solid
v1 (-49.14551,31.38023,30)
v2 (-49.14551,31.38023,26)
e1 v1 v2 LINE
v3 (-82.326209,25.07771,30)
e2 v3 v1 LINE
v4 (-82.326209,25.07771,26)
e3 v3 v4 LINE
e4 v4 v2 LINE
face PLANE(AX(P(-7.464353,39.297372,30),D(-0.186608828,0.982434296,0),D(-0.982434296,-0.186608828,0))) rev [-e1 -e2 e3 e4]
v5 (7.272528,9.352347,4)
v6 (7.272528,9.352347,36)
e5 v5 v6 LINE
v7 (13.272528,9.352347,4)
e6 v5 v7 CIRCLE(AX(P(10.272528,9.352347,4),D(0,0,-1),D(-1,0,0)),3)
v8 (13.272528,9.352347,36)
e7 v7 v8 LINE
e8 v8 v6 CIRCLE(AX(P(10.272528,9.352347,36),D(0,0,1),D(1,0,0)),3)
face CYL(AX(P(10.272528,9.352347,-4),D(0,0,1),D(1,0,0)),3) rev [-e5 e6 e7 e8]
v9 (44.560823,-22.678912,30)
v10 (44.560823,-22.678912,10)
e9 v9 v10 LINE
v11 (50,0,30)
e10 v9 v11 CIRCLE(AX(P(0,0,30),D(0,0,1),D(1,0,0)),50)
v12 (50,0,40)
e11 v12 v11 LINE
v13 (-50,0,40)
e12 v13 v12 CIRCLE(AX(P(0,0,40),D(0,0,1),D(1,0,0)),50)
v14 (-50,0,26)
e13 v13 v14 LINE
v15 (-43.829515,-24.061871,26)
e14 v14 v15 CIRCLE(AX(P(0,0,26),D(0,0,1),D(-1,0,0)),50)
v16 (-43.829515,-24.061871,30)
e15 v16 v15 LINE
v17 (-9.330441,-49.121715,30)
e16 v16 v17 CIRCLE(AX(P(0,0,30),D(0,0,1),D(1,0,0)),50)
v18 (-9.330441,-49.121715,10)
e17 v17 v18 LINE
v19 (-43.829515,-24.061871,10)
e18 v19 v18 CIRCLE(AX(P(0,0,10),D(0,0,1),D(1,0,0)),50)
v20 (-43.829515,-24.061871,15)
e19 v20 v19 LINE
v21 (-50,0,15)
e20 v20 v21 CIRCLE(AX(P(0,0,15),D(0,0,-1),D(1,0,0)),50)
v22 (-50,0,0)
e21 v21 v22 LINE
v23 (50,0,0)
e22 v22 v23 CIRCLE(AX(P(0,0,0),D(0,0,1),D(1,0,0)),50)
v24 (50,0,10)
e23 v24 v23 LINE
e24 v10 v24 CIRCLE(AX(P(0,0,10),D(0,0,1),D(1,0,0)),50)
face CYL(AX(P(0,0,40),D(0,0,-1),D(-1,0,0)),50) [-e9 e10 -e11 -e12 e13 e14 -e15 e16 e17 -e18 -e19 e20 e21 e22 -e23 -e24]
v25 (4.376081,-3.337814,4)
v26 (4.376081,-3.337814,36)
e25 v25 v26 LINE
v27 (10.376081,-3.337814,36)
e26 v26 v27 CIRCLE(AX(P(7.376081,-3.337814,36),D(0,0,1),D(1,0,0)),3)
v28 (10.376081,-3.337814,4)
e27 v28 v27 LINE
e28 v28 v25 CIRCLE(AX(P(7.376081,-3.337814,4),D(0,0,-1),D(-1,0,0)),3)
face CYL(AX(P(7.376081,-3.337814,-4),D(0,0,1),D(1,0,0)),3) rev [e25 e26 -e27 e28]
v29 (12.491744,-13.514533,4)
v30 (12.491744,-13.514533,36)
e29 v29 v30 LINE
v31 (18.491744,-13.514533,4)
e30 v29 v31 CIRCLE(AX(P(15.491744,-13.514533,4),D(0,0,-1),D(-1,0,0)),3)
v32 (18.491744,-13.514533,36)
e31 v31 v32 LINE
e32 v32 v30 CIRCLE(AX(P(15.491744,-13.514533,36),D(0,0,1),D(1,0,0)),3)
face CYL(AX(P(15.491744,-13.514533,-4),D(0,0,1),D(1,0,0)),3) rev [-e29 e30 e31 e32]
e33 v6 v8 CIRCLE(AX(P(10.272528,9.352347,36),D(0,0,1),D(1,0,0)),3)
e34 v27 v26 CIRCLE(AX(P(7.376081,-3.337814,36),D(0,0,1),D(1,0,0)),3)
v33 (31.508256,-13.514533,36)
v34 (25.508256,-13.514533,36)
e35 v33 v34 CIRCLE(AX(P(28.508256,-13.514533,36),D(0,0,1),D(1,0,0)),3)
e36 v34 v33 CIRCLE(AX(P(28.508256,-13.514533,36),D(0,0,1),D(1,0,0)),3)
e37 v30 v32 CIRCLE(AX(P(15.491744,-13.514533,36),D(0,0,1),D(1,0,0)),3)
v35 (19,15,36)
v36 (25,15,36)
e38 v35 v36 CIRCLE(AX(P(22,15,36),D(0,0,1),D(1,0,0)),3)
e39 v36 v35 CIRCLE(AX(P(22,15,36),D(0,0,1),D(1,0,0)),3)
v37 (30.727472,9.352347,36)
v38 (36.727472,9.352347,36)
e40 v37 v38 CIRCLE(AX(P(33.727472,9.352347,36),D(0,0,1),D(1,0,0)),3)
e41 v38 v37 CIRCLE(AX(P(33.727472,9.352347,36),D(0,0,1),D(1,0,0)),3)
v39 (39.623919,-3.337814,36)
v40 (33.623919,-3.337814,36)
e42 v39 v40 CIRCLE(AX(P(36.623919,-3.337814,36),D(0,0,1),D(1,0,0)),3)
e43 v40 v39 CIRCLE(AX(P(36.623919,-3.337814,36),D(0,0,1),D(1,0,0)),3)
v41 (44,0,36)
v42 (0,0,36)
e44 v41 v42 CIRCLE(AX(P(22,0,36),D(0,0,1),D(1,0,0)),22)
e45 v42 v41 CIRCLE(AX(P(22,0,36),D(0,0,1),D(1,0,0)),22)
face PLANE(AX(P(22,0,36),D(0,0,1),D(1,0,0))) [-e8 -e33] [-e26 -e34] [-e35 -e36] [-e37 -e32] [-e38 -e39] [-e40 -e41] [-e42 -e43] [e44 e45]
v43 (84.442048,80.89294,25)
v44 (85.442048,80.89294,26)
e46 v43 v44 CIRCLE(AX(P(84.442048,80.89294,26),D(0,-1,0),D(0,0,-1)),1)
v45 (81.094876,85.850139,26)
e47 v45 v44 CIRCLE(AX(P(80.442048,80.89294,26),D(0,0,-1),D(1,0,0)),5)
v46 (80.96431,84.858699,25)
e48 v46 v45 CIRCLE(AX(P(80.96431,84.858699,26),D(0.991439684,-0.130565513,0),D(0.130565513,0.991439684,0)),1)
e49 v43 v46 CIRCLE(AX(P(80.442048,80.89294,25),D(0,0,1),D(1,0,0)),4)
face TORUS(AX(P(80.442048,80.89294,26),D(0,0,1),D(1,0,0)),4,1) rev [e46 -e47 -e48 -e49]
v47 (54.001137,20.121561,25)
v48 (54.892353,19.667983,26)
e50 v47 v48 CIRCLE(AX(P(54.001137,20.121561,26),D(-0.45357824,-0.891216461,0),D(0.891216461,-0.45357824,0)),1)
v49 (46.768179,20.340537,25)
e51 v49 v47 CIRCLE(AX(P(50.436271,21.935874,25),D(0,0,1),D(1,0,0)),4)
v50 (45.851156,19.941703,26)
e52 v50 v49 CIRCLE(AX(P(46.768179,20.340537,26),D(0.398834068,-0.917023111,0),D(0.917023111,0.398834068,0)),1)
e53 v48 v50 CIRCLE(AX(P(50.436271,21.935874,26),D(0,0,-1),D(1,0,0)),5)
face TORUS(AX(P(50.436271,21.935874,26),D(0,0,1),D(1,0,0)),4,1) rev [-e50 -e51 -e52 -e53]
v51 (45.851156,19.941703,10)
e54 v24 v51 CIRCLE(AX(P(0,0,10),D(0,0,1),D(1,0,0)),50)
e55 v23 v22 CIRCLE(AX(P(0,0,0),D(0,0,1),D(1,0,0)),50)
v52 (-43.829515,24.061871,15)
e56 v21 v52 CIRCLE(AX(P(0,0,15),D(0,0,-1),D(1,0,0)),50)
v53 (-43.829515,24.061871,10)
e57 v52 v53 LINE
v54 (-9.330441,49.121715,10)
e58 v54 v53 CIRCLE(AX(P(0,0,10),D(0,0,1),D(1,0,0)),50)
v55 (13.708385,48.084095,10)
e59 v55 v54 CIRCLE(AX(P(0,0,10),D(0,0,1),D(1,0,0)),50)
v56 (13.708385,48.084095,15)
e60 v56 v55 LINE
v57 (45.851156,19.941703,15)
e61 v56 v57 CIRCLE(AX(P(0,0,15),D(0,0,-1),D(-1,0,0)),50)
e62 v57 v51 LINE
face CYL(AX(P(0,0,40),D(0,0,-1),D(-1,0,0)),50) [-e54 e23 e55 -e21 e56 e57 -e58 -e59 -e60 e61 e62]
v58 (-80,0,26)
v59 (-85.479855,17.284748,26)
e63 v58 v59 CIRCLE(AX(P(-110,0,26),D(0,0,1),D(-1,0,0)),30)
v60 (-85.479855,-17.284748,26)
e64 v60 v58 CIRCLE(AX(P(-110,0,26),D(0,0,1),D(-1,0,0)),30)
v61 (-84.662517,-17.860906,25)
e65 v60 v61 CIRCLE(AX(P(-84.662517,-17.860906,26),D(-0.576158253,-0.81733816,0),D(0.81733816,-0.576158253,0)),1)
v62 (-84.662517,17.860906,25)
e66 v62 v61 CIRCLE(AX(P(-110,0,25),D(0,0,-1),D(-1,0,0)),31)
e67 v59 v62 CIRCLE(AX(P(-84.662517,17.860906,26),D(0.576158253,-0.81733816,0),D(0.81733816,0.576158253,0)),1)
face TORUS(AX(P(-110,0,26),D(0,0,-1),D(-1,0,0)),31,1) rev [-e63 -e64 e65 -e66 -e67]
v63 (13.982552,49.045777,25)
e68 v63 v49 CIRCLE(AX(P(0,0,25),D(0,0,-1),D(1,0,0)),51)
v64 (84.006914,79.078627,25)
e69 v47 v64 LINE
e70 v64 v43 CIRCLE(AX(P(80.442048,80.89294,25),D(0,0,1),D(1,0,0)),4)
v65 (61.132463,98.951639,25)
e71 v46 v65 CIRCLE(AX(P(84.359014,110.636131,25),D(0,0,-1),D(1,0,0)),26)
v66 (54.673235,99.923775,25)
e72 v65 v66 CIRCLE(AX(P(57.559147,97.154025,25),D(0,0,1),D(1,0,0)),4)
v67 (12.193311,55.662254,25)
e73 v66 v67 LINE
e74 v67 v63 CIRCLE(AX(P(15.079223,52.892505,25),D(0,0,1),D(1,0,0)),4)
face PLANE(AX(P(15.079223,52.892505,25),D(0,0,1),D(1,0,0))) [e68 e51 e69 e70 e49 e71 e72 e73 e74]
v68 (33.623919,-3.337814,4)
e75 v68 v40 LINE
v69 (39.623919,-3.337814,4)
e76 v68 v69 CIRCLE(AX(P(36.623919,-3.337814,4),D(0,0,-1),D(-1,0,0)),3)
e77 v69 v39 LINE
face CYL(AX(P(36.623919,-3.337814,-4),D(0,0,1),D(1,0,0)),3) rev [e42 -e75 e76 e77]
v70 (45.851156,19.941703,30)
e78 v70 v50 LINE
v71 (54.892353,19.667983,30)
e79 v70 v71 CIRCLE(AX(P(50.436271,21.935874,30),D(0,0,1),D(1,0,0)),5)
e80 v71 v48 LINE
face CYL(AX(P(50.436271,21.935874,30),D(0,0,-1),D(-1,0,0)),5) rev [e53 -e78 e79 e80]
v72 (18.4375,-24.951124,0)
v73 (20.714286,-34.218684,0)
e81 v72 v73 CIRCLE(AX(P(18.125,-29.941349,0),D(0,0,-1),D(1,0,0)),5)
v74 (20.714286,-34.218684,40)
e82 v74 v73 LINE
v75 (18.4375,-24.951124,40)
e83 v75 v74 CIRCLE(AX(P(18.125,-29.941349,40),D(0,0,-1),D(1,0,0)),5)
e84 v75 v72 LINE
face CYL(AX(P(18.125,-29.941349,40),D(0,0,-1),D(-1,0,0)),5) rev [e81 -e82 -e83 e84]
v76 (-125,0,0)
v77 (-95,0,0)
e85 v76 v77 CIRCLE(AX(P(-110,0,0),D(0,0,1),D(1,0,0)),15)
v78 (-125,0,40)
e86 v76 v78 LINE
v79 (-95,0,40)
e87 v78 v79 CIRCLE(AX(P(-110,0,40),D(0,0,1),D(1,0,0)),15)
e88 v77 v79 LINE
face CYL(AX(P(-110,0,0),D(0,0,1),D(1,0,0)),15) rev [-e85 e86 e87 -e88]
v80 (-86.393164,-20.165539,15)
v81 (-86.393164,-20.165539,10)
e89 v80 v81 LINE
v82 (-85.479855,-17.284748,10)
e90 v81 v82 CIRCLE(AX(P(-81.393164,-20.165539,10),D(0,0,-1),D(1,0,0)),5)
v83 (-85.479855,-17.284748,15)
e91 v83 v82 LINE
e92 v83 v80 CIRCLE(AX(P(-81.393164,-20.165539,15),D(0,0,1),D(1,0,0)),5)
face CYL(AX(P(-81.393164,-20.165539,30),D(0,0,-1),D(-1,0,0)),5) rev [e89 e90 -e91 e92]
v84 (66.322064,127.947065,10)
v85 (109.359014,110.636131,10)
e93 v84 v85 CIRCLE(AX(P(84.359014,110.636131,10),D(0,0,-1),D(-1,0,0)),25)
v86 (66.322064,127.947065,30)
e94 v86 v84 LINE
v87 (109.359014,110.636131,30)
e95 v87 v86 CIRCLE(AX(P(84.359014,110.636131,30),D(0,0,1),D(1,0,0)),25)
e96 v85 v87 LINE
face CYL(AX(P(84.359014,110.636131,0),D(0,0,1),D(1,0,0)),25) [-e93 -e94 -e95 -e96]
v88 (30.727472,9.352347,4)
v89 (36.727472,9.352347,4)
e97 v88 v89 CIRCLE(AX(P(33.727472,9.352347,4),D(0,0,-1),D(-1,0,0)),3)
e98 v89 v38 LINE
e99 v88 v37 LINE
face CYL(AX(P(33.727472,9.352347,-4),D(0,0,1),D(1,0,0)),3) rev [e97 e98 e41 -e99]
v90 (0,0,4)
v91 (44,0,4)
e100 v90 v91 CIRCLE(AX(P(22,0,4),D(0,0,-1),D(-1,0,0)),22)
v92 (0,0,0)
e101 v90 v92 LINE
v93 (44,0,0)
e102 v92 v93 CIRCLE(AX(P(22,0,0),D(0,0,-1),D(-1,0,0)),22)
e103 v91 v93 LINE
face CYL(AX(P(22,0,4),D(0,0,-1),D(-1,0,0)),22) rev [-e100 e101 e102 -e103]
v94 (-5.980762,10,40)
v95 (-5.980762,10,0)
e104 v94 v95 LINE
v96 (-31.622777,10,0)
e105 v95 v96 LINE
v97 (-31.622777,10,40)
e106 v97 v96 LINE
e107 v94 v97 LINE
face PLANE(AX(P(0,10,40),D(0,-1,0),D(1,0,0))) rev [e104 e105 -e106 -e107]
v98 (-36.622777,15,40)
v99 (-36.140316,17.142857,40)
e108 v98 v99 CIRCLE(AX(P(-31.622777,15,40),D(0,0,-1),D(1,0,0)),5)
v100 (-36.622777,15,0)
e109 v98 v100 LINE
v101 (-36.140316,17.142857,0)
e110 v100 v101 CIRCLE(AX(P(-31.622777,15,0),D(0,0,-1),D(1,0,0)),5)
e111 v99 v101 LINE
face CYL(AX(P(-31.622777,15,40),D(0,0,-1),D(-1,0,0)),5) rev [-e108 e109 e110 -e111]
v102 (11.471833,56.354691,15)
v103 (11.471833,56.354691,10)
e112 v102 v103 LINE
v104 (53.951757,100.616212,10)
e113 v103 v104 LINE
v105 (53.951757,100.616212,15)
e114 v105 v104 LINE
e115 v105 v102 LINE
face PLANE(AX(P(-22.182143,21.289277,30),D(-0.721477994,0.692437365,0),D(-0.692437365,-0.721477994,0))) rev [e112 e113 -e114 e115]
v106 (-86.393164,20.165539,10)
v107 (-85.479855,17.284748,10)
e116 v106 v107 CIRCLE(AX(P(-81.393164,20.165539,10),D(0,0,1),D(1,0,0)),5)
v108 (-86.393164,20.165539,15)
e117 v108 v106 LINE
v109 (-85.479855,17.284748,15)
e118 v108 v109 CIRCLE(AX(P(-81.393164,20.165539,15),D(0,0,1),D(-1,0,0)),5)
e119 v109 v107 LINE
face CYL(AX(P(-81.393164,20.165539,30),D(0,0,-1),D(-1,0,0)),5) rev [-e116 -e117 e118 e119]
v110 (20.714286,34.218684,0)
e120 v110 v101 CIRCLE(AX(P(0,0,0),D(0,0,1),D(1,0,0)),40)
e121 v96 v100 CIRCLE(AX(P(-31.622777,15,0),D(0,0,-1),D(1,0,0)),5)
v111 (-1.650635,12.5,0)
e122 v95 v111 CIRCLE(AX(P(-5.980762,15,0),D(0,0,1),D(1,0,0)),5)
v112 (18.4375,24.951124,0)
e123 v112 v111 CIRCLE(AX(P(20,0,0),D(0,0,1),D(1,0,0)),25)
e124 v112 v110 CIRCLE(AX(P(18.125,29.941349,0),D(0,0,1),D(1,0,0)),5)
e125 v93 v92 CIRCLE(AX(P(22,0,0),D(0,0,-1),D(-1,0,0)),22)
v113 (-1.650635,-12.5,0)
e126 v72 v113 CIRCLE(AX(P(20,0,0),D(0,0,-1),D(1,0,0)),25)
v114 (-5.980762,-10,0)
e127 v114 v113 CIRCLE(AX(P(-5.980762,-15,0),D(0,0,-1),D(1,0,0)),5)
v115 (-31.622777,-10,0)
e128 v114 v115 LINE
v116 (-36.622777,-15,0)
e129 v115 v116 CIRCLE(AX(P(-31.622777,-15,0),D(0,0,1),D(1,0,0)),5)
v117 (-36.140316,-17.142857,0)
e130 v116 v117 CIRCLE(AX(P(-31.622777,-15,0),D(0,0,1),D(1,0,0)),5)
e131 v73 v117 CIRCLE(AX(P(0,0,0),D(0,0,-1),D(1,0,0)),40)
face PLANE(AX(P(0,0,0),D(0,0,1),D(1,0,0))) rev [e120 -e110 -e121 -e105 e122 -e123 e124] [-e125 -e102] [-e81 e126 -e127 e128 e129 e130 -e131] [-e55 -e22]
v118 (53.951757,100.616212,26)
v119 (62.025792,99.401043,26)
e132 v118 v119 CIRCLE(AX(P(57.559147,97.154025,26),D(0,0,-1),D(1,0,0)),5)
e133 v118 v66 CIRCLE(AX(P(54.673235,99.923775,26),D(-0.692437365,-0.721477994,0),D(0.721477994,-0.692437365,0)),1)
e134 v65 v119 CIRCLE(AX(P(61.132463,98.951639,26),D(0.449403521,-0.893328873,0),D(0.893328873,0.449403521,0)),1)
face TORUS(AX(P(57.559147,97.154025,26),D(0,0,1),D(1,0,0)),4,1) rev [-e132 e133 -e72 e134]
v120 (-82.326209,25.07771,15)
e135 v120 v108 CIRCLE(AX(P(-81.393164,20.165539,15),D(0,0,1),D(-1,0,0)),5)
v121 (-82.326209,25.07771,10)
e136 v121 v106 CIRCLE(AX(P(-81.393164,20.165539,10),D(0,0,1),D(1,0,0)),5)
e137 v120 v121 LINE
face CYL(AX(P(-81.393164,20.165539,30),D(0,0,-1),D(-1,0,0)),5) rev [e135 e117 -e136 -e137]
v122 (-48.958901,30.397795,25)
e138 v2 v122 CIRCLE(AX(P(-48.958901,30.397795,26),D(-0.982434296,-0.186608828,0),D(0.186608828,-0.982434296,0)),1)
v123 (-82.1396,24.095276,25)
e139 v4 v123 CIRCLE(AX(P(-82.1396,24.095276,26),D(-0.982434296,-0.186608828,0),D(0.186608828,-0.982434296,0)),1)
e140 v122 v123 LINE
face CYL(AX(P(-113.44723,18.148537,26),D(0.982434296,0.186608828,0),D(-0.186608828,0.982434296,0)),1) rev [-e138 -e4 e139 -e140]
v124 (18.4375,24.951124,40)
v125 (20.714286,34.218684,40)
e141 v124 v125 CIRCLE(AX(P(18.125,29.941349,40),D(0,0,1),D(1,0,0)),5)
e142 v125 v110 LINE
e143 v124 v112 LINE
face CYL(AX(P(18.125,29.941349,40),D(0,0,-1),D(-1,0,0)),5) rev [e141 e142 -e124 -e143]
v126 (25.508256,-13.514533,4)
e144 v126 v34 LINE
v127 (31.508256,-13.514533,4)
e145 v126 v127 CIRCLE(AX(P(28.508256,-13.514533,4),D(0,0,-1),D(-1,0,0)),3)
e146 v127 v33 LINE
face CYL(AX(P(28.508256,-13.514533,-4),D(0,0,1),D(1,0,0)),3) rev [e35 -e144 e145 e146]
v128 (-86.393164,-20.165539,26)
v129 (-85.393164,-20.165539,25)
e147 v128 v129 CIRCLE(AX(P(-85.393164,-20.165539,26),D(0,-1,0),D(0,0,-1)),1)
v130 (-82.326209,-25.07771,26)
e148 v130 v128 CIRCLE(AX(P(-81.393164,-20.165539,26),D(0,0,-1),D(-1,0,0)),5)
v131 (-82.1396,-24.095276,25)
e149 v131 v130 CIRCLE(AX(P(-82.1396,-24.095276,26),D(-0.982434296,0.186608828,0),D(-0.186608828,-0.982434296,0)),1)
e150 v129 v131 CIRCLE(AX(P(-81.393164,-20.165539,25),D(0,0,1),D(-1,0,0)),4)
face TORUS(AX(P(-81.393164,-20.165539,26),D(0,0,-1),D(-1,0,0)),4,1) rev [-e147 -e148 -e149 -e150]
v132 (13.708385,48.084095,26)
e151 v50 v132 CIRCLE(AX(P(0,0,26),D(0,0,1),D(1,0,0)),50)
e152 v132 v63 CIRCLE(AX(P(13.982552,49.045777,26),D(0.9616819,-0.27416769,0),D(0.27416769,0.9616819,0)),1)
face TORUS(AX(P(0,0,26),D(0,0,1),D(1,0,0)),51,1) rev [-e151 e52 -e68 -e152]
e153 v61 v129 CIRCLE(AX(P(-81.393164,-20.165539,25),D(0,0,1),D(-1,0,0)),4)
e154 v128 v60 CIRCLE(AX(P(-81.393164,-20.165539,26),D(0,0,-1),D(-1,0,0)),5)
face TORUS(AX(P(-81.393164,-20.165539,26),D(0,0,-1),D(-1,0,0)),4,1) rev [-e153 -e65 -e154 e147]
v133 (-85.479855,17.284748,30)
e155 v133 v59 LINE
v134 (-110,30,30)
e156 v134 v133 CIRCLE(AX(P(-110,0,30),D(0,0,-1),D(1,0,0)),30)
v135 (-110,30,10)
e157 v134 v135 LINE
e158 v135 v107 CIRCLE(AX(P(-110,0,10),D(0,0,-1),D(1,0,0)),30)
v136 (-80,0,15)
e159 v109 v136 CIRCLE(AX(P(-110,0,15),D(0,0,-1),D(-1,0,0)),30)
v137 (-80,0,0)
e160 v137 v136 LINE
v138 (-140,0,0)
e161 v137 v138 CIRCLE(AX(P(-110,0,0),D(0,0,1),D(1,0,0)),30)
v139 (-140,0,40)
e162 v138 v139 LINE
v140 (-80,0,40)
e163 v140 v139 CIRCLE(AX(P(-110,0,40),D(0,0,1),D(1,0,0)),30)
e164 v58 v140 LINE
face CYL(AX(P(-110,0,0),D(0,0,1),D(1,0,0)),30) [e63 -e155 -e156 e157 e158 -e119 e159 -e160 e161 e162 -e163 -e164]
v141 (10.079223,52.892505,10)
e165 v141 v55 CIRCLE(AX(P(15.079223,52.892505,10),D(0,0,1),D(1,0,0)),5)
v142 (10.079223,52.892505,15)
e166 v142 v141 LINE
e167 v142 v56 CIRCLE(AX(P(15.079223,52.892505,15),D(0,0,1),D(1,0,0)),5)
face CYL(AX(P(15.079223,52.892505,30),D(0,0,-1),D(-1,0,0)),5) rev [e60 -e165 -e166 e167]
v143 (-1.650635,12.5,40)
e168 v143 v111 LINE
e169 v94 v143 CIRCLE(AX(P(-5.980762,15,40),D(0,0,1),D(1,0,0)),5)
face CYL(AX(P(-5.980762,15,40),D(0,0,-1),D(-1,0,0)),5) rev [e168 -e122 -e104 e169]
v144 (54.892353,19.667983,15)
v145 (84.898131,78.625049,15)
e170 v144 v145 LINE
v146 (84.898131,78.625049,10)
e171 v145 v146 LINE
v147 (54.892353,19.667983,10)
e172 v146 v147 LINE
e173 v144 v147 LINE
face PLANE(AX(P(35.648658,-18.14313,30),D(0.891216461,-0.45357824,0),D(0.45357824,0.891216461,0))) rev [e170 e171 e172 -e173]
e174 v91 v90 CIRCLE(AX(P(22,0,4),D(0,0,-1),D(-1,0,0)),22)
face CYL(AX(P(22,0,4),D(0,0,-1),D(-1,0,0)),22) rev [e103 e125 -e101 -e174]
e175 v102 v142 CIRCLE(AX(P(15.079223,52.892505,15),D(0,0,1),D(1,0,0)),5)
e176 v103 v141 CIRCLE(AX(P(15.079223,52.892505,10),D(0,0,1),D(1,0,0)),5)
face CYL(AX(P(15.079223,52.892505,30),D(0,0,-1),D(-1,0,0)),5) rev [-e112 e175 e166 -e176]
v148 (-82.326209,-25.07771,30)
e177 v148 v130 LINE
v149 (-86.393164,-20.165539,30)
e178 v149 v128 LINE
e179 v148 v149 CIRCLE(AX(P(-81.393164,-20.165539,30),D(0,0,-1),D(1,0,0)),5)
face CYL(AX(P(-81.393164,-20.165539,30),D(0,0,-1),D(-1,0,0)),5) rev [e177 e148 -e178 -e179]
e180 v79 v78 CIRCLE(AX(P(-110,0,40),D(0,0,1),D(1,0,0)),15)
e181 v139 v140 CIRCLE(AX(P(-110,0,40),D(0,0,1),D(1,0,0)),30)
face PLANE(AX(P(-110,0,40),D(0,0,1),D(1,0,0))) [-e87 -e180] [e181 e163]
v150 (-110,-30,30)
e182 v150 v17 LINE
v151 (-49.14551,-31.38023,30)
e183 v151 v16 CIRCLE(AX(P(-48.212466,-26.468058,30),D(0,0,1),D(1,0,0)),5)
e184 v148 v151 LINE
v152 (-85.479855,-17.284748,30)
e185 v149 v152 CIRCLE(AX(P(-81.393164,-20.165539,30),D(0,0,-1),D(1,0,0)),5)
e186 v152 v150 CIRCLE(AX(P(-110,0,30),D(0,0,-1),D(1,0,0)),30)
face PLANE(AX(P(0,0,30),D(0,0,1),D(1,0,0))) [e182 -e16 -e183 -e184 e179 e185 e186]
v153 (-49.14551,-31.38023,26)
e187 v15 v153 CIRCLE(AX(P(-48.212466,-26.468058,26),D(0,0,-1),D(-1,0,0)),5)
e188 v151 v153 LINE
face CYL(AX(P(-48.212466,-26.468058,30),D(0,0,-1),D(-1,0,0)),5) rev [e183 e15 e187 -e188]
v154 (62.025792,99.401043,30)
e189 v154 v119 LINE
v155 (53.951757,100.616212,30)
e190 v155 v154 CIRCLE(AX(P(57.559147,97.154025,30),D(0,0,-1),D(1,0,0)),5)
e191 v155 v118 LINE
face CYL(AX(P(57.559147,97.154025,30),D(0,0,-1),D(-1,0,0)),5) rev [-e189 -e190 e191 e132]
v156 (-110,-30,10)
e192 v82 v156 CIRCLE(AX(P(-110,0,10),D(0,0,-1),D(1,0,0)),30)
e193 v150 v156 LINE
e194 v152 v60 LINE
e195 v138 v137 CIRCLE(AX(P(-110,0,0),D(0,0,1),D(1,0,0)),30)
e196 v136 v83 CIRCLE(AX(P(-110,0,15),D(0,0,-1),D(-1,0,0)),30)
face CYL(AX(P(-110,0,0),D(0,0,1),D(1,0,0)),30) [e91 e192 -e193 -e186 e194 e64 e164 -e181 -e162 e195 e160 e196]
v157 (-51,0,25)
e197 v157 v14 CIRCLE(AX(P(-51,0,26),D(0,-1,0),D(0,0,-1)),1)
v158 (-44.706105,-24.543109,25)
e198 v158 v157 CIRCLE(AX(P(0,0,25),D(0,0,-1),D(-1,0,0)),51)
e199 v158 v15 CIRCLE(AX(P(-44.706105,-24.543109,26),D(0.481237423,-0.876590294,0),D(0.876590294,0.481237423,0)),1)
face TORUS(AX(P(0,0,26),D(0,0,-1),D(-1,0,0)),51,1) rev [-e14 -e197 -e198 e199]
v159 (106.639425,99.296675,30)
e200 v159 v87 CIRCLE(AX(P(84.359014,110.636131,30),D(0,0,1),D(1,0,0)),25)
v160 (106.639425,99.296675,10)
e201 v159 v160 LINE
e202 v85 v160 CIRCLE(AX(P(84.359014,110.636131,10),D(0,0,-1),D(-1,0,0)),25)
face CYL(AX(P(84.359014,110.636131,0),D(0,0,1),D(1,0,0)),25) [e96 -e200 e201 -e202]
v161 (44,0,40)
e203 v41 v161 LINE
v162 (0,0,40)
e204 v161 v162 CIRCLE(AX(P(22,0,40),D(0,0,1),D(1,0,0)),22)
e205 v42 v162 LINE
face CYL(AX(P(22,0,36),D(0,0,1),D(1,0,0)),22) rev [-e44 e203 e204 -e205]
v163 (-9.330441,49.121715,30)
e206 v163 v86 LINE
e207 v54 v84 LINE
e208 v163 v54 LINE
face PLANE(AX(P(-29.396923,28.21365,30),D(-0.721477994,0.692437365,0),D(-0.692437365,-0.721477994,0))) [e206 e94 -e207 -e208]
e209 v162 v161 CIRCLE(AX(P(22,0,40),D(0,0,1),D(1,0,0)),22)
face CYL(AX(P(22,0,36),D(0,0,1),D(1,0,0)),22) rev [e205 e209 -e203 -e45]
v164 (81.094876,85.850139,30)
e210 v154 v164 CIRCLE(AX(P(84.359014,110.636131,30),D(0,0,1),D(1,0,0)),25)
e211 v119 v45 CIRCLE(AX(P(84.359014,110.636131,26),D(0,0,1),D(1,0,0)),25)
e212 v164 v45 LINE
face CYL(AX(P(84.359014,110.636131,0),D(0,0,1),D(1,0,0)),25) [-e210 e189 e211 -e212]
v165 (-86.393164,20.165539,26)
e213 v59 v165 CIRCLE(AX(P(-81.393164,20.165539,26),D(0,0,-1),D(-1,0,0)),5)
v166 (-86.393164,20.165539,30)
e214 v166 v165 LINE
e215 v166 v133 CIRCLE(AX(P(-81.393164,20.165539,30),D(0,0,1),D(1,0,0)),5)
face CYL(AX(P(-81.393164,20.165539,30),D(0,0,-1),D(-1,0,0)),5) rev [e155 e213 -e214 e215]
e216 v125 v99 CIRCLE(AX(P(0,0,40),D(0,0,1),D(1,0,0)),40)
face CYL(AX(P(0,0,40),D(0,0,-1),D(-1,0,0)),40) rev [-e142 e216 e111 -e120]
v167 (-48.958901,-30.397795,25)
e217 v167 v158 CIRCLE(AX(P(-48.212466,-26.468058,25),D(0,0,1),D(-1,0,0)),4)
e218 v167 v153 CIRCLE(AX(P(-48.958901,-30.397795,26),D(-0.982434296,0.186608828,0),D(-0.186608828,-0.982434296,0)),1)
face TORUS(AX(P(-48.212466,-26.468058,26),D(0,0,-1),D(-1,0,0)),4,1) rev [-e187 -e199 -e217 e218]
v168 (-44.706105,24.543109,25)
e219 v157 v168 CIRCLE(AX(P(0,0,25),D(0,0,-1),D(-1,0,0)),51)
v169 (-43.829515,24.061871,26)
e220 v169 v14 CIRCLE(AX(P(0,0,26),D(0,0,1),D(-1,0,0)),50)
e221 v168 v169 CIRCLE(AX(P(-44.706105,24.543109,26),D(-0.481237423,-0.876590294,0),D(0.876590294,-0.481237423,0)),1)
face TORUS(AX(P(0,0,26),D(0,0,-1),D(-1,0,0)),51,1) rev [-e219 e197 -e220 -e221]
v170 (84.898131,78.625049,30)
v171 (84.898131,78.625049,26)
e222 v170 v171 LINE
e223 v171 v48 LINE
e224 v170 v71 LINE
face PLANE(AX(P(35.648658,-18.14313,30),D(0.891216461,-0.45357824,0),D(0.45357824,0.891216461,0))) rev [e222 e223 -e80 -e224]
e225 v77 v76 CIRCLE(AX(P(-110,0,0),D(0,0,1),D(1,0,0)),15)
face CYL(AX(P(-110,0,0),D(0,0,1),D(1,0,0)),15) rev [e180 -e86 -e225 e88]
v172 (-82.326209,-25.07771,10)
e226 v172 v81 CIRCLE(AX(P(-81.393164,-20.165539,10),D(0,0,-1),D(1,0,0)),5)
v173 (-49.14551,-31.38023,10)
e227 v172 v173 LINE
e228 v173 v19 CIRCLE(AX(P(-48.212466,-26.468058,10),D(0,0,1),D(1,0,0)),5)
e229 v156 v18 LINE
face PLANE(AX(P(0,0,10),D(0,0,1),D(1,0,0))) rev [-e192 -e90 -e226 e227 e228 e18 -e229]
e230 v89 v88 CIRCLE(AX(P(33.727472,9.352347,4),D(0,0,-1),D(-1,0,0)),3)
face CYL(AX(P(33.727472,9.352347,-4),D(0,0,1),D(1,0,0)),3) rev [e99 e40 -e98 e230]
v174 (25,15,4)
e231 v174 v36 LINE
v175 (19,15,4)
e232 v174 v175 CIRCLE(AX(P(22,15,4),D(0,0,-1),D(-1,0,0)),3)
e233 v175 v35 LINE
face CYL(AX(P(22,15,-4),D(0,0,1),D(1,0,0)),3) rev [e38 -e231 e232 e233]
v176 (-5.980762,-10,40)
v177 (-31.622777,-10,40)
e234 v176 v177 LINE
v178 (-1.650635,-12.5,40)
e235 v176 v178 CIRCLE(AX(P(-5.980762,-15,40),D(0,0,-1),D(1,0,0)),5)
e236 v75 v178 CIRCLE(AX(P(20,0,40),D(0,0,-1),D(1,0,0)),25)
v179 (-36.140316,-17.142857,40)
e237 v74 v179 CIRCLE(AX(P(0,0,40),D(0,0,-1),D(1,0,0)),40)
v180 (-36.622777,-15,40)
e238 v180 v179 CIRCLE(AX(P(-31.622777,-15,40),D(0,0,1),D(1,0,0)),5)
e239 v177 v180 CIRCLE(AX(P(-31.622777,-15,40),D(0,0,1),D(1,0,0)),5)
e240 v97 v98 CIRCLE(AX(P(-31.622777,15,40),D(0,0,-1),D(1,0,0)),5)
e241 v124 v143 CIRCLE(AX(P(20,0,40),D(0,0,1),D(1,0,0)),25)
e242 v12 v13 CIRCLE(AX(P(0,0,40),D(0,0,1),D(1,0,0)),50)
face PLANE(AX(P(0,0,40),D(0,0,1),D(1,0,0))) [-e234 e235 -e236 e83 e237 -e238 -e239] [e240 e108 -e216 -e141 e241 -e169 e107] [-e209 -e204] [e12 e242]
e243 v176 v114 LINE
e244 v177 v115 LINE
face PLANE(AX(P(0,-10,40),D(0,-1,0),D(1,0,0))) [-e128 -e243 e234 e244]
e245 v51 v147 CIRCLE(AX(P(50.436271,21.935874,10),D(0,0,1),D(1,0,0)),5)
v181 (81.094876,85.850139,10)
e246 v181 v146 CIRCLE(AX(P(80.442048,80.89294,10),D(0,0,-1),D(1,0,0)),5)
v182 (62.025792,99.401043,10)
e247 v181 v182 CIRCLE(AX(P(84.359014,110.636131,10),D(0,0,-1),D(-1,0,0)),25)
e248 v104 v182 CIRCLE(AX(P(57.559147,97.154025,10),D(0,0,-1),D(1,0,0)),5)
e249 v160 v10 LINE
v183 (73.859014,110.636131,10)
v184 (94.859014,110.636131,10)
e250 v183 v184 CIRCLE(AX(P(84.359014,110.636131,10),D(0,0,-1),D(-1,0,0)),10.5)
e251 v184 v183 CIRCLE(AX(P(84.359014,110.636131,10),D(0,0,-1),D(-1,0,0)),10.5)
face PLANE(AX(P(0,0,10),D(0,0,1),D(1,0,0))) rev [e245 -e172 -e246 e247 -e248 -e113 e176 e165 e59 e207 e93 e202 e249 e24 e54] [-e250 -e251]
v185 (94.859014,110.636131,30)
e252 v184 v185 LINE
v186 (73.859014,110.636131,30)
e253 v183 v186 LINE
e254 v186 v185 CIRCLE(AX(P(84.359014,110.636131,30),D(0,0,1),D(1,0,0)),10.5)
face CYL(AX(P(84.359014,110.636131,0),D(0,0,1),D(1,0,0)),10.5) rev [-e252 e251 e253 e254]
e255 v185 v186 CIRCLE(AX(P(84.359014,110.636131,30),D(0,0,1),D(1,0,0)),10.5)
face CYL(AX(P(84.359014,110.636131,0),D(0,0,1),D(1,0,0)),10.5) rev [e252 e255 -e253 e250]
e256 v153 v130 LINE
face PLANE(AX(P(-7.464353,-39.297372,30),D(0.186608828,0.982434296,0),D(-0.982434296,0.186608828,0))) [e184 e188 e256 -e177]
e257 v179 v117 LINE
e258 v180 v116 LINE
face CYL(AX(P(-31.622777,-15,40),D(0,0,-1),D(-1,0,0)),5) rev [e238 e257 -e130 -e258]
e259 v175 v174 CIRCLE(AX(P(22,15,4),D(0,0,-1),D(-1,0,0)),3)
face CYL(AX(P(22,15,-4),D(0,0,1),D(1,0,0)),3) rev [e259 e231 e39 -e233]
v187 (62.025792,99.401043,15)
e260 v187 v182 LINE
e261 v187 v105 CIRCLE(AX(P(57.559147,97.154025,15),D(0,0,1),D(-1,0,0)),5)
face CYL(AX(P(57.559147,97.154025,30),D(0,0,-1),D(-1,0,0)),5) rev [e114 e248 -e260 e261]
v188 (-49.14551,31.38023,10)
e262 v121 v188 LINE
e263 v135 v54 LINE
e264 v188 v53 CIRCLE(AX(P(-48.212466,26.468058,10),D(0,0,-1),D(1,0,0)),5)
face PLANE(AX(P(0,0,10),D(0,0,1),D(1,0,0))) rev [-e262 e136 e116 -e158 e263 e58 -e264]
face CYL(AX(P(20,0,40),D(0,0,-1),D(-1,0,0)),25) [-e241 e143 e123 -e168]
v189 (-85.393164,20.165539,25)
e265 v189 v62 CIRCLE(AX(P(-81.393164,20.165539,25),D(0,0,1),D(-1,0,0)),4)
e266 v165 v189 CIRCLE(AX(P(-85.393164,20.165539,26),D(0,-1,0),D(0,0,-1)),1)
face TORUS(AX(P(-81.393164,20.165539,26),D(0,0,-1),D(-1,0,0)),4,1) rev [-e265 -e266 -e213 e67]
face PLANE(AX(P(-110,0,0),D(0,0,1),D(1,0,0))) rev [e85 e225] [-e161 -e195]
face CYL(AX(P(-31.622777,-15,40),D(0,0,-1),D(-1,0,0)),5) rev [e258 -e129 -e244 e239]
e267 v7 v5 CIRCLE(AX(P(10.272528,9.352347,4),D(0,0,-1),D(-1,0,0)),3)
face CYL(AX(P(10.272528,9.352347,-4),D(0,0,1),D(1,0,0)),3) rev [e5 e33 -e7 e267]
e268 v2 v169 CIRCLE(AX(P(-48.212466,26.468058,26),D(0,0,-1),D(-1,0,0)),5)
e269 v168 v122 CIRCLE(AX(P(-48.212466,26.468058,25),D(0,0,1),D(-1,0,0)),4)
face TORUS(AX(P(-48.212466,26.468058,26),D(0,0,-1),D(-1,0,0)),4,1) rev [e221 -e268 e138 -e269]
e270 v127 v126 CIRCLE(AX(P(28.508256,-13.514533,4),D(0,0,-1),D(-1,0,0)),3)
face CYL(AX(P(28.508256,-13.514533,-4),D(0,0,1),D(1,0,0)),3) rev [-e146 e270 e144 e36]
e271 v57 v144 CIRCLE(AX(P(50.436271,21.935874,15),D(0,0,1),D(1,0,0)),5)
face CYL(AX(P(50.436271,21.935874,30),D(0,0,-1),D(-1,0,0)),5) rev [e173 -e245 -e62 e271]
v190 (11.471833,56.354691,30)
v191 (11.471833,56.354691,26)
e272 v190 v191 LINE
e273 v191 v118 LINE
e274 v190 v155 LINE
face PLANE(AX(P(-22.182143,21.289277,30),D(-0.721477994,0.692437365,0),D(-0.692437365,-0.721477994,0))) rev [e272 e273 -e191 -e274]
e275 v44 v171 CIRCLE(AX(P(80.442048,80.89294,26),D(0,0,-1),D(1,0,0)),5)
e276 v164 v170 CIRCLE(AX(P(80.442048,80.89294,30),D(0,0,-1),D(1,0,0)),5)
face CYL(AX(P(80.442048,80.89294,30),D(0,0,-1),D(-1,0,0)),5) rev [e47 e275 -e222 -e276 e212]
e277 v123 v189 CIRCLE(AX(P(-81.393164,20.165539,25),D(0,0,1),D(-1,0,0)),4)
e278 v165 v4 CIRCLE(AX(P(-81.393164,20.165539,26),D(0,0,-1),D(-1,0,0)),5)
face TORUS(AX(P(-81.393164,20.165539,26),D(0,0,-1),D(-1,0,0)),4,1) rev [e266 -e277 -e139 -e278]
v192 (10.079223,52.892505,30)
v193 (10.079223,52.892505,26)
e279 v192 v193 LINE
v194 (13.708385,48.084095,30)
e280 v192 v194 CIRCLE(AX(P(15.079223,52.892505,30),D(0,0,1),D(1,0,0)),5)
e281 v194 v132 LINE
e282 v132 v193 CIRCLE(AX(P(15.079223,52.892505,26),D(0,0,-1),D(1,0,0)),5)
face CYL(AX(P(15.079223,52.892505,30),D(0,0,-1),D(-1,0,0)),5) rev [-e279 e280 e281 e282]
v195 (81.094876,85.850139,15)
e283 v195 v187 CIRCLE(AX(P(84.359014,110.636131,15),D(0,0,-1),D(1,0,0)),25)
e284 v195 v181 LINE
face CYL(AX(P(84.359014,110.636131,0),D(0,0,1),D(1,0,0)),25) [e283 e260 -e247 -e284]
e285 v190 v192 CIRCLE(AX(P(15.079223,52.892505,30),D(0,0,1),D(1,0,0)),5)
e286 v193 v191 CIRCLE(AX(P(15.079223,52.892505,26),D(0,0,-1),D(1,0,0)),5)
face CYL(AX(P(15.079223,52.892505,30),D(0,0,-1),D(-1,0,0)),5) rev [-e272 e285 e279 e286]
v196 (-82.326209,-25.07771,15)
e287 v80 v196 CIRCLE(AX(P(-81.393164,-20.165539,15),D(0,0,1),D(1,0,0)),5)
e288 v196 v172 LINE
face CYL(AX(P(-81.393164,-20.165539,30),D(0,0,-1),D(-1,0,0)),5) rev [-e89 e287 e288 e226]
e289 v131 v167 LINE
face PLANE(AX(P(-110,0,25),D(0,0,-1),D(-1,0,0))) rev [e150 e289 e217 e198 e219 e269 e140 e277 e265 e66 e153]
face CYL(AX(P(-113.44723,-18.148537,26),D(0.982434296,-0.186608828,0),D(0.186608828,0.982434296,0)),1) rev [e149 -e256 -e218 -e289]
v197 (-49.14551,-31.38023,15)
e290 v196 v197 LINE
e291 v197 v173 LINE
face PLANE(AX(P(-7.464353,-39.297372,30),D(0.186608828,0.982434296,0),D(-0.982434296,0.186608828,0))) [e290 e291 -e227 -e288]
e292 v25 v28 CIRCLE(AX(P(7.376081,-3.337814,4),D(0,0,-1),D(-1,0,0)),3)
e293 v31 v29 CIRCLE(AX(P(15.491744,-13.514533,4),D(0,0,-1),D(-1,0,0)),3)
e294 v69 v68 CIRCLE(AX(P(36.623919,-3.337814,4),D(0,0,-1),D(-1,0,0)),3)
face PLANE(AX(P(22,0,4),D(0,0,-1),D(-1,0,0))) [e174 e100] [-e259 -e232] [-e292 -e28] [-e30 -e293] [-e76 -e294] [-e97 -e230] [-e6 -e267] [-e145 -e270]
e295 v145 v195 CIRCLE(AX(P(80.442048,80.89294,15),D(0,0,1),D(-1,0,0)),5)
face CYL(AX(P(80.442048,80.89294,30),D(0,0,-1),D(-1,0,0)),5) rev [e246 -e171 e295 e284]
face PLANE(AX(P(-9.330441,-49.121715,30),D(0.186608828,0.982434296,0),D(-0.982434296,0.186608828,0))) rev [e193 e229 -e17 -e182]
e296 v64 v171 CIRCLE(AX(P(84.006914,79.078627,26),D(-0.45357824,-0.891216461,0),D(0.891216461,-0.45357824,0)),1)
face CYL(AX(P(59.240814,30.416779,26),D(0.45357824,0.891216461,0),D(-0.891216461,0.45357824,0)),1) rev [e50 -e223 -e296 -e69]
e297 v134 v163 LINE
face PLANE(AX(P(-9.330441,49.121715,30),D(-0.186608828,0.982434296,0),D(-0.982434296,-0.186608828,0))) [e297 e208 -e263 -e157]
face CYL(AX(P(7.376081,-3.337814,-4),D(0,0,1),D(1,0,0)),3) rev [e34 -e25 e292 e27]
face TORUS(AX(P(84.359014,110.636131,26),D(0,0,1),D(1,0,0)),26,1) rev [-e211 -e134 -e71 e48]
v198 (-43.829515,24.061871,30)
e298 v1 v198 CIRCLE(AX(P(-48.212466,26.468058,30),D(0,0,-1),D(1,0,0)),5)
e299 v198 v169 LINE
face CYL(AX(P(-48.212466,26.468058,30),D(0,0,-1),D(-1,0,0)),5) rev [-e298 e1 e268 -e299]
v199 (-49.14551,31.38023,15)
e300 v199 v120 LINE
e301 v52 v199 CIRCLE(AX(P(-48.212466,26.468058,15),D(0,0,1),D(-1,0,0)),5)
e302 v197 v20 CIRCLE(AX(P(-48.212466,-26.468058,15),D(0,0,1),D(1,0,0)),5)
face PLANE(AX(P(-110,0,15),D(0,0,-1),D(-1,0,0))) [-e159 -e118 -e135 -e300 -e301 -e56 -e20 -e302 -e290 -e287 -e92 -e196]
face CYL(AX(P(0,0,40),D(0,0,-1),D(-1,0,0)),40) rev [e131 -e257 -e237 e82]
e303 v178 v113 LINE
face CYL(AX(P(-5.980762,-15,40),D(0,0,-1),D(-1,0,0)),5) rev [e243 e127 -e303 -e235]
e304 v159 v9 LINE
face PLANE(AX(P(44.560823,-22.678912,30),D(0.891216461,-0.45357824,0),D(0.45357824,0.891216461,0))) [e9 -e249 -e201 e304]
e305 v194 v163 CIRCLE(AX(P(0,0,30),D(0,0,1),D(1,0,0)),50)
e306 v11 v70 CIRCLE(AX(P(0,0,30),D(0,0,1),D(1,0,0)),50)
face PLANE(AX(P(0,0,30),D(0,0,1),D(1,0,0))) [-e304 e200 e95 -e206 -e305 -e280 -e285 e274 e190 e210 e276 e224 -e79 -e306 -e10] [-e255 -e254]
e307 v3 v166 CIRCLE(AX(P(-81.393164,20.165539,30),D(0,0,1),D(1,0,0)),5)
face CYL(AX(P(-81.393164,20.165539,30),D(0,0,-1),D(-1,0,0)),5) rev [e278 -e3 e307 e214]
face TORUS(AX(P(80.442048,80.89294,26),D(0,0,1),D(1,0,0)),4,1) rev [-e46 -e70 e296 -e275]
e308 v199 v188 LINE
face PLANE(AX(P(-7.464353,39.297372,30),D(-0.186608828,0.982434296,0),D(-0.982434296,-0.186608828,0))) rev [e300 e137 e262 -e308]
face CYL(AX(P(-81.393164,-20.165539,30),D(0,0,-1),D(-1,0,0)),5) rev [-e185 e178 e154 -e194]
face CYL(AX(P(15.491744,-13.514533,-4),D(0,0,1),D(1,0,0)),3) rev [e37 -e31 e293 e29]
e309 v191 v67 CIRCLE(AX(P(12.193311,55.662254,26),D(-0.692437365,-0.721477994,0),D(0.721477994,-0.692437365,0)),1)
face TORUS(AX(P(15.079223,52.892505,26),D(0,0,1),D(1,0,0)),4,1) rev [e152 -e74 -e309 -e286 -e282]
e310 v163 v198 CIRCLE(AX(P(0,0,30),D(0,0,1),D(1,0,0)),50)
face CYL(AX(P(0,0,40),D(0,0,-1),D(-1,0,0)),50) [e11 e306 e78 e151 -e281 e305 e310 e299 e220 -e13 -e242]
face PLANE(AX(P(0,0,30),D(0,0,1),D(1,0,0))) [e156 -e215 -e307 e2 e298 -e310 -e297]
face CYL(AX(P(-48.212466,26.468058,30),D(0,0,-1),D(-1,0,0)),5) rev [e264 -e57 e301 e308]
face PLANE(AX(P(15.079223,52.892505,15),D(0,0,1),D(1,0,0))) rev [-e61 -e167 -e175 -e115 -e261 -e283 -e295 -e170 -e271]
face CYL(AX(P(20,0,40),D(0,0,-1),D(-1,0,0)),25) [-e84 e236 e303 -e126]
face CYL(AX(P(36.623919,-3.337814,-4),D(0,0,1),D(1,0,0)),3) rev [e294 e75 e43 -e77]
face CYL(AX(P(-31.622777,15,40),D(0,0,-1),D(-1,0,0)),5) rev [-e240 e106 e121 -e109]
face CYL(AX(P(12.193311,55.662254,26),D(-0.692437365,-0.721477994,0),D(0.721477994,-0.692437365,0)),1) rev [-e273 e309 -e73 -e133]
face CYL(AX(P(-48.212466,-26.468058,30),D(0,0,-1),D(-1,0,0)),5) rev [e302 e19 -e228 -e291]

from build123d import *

# Parameters (mm, degrees)
LEVER_BODY_PROFILE_R      = 50
LEVER_BODY_DEPTH          = 40
FRONT_POCKET_PROFILE_R    = 22
FRONT_POCKET_PROFILE_R_2  = 3
FRONT_POCKET_4MM_DEPTH    = 4
HUB_THROUGH_CUT_PROFILE_R = 3
HUB_THROUGH_CUT_DEPTH     = 44
REAR_START                = -4
REAR_POCKET_PROFILE_R     = 22
REAR_POCKET_PROFILE_R_2   = 3
REAR_POCKET_4MM_DEPTH     = 4
ARM_BOSS_PROFILE_R        = 30
ARM_BOSS_PROFILE_R_2      = 15
ARM_BOSS_DEPTH            = 40
WEB_ARM_PROFILE_R         = 25
WEB_ARM_PROFILE_R_2       = 10.5
TRIANGULAR_WEB_ARM_DEPTH  = 40
FRONT_HUB_BOSS_DEPTH      = 10
REAR_HUB_FLANGE_DEPTH     = 5
HUB_EDGE_FILLET_R1_A_R    = 1
HUB_EDGE_FILLET_R1_B_R    = 1
WEB_ARM_CUT_A_PROFILE_R   = 25
WEB_ARM_CUT_A_PROFILE_R_2 = 10.5
WEB_ARM_CUT_A_DEPTH       = 10
WEB_START                 = -10
WEB_ARM_CUT_B_PROFILE_R   = 25
WEB_ARM_CUT_B_PROFILE_R_2 = 10.5
WEB_ARM_CUT_B_DEPTH       = 10


with BuildPart() as part:
    # Lever Body Profile → Lever Body (new body)
    with BuildSketch(Plane.XY):
        Circle(LEVER_BODY_PROFILE_R)
        with BuildLine():
            Line((-5.980762114, 10), (-31.622776602, 10))
            ThreePointArc((-31.622776602, 10), (-35.848547875, 12.327387581), (-36.140316116, 17.142857143))
            ThreePointArc((-36.140316116, 17.142857143), (-11.505936436, 38.309443049), (20.714285714, 34.218684477))
            ThreePointArc((20.714285714, 34.218684477), (22.980616225, 28.748457023), (18.4375, 24.951124098))
            ThreePointArc((18.4375, 24.951124098), (6.829197706, 21.249234503), (-1.650635095, 12.5))
            ThreePointArc((-1.650635095, 12.5), (-3.480762114, 10.669872981), (-5.980762114, 10))
        make_face(mode=Mode.SUBTRACT)
        with BuildLine():
            Line((-5.980762114, -10), (-31.622776602, -10))
            ThreePointArc((-31.622776602, -10), (-35.848547875, -12.327387581), (-36.140316116, -17.142857143))
            ThreePointArc((-36.140316116, -17.142857143), (-11.505936436, -38.309443049), (20.714285714, -34.218684477))
            ThreePointArc((20.714285714, -34.218684477), (22.980616225, -28.748457023), (18.4375, -24.951124098))
            ThreePointArc((18.4375, -24.951124098), (6.829197706, -21.249234503), (-1.650635095, -12.5))
            ThreePointArc((-1.650635095, -12.5), (-3.480762114, -10.669872981), (-5.980762114, -10))
        make_face(mode=Mode.SUBTRACT)
    extrude(amount=LEVER_BODY_DEPTH)

    # Front Pocket Profile → Front Pocket 4mm (cut)
    with BuildSketch(Plane.XY.offset(40)):
        with Locations((22, 0)):
            Circle(FRONT_POCKET_PROFILE_R)
        with Locations((22, 15)):
            Circle(FRONT_POCKET_PROFILE_R_2, mode=Mode.SUBTRACT)
        with Locations((33.727472237, 9.352347028)):
            Circle(FRONT_POCKET_PROFILE_R_2, mode=Mode.SUBTRACT)
        with Locations((36.623918683, -3.337814009)):
            Circle(FRONT_POCKET_PROFILE_R_2, mode=Mode.SUBTRACT)
        with Locations((28.508256087, -13.514533019)):
            Circle(FRONT_POCKET_PROFILE_R_2, mode=Mode.SUBTRACT)
        with Locations((15.491743913, -13.514533019)):
            Circle(FRONT_POCKET_PROFILE_R_2, mode=Mode.SUBTRACT)
        with Locations((7.376081317, -3.337814009)):
            Circle(FRONT_POCKET_PROFILE_R_2, mode=Mode.SUBTRACT)
        with Locations((10.272527763, 9.352347028)):
            Circle(FRONT_POCKET_PROFILE_R_2, mode=Mode.SUBTRACT)
    extrude(amount=-FRONT_POCKET_4MM_DEPTH, mode=Mode.SUBTRACT)

    # Hub Through Cut Profile → Hub Through Cut (cut)
    with BuildSketch(Plane.XY.offset(40)):
        with Locations((22, 15)):
            Circle(HUB_THROUGH_CUT_PROFILE_R)
        with Locations((33.727472237, 9.352347028)):
            Circle(HUB_THROUGH_CUT_PROFILE_R)
        with Locations((36.623918683, -3.337814009)):
            Circle(HUB_THROUGH_CUT_PROFILE_R)
        with Locations((28.508256087, -13.514533019)):
            Circle(HUB_THROUGH_CUT_PROFILE_R)
        with Locations((15.491743913, -13.514533019)):
            Circle(HUB_THROUGH_CUT_PROFILE_R)
        with Locations((7.376081317, -3.337814009)):
            Circle(HUB_THROUGH_CUT_PROFILE_R)
        with Locations((10.272527763, 9.352347028)):
            Circle(HUB_THROUGH_CUT_PROFILE_R)
    extrude(amount=-HUB_THROUGH_CUT_DEPTH, mode=Mode.SUBTRACT)

    # Rear Pocket Profile → Rear Pocket 4mm (cut)
    with BuildSketch(Plane(origin=(0, 0, 0), x_dir=(-1, 0, 0), z_dir=(0, 0, -1)).offset(REAR_START)):
        with Locations(Location((-22, 0, 0), (0, 0, 180))):
            Circle(REAR_POCKET_PROFILE_R)
        with Locations(Location((-22, 15, 0), (0, 0, 180))):
            Circle(REAR_POCKET_PROFILE_R_2, mode=Mode.SUBTRACT)
        with Locations(Location((-10.272527763, 9.352347028, 0), (0, 0, 180))):
            Circle(REAR_POCKET_PROFILE_R_2, mode=Mode.SUBTRACT)
        with Locations(Location((-7.376081317, -3.337814009, 0), (0, 0, 180))):
            Circle(REAR_POCKET_PROFILE_R_2, mode=Mode.SUBTRACT)
        with Locations(Location((-15.491743913, -13.514533019, 0), (0, 0, 180))):
            Circle(REAR_POCKET_PROFILE_R_2, mode=Mode.SUBTRACT)
        with Locations(Location((-28.508256087, -13.514533019, 0), (0, 0, 180))):
            Circle(REAR_POCKET_PROFILE_R_2, mode=Mode.SUBTRACT)
        with Locations(Location((-36.623918683, -3.337814009, 0), (0, 0, 180))):
            Circle(REAR_POCKET_PROFILE_R_2, mode=Mode.SUBTRACT)
        with Locations(Location((-33.727472237, 9.352347028, 0), (0, 0, 180))):
            Circle(REAR_POCKET_PROFILE_R_2, mode=Mode.SUBTRACT)
    extrude(amount=REAR_POCKET_4MM_DEPTH, mode=Mode.SUBTRACT)



with BuildPart() as body_2:
    # Arm Boss Profile → Arm Boss (new body)
    with BuildSketch(Plane.XY.offset(40)):
        with Locations((-110, 0)):
            Circle(ARM_BOSS_PROFILE_R)
        with Locations((-110, 0)):
            Circle(ARM_BOSS_PROFILE_R_2, mode=Mode.SUBTRACT)
    extrude(amount=-ARM_BOSS_DEPTH)


with BuildPart() as body_3:
    # Web Arm Profile → Triangular Web Arm (new body)
    with BuildSketch(Plane.XY.offset(40)):
        with Locations((84.359013574, 110.636130744)):
            Circle(WEB_ARM_PROFILE_R)
        with Locations((84.359013574, 110.636130744)):
            Circle(WEB_ARM_PROFILE_R_2, mode=Mode.SUBTRACT)
    extrude(amount=-TRIANGULAR_WEB_ARM_DEPTH)


with BuildPart() as part_1:
    add(part.part)

    add(body_2.part)  # Front Hub Boss merges body 2

    add(body_3.part)  # Front Hub Boss merges body 3
    # Front Hub Boss Profile → Front Hub Boss (add, symmetric)
    with BuildSketch(Plane.XY.offset(20)):
        with BuildLine():
            Line((-9.330441424, 49.121714779), (-110, 30))
            ThreePointArc((-110, 30), (-96.189540691, 26.632146246), (-85.479855197, 17.284747578))
            ThreePointArc((-85.479855197, 17.284747578), (-86.028032441, 22.041171589), (-82.326208539, 25.077710319))
            Line((-82.326208539, 25.077710319), (-49.145510288, 31.38022974))
            ThreePointArc((-49.145510288, 31.38022974), (-44.167091223, 29.4065854), (-43.829514678, 24.061871148))
            ThreePointArc((-43.829514678, 24.061871148), (-29.385271377, 40.453749222), (-9.330441424, 49.121714779))
        make_face()
        with BuildLine():
            ThreePointArc((-82.326208539, -25.077710319), (-86.028032441, -22.041171589), (-85.479855197, -17.284747578))
            ThreePointArc((-85.479855197, -17.284747578), (-96.189540691, -26.632146246), (-110, -30))
            Line((-110, -30), (-9.330441424, -49.121714779))
            ThreePointArc((-9.330441424, -49.121714779), (-29.385271377, -40.453749222), (-43.829514678, -24.061871148))
            ThreePointArc((-43.829514678, -24.061871148), (-44.167091223, -29.4065854), (-49.145510288, -31.38022974))
            Line((-49.145510288, -31.38022974), (-82.326208539, -25.077710319))
        make_face()
        with BuildLine():
            Line((66.322063718, 127.947064858), (-9.330441424, 49.121714779))
            ThreePointArc((-9.330441424, 49.121714779), (2.249613331, 49.949366761), (13.708384523, 48.084095019))
            ThreePointArc((13.708384523, 48.084095019), (10.252590563, 51.587276744), (11.471833004, 56.354691343))
            Line((11.471833004, 56.354691343), (53.95175742, 100.616211925))
            ThreePointArc((53.95175742, 100.616211925), (58.303283523, 102.098341173), (62.025791755, 99.401042709))
            ThreePointArc((62.025791755, 99.401042709), (59.637433216, 114.356811406), (66.322063718, 127.947064858))
        make_face()
        with BuildLine():
            ThreePointArc((54.892353403, 19.667982557), (50.284966201, 16.9381636), (45.851155545, 19.941703417))
            ThreePointArc((45.851155545, 19.941703417), (48.951801689, 10.184356208), (50, 0))
            ThreePointArc((50, 0), (48.621194719, -11.661021572), (44.560823036, -22.67891202))
            Line((44.560823036, -22.67891202), (106.639425092, 99.296674734))
            ThreePointArc((106.639425092, 99.296674734), (96.00405542, 88.513902095), (81.094875761, 85.850138645))
            ThreePointArc((81.094875761, 85.850138645), (84.866493928, 83.221948595), (84.898130502, 78.625049023))
            Line((84.898130502, 78.625049023), (54.892353403, 19.667982557))
        make_face()
    extrude(amount=FRONT_HUB_BOSS_DEPTH, both=True)

    # Rear Hub Flange Profile → Rear Hub Flange (add, symmetric)
    with BuildSketch(Plane.XY.offset(20)):
        with BuildLine():
            Line((-82.326208539, 25.077710319), (-49.145510288, 31.38022974))
            ThreePointArc((-49.145510288, 31.38022974), (-44.167091223, 29.4065854), (-43.829514678, 24.061871148))
            ThreePointArc((-43.829514678, 24.061871148), (-50, 0), (-43.829514678, -24.061871148))
            ThreePointArc((-43.829514678, -24.061871148), (-44.167091223, -29.4065854), (-49.145510288, -31.38022974))
            Line((-49.145510288, -31.38022974), (-82.326208539, -25.077710319))
            ThreePointArc((-82.326208539, -25.077710319), (-86.028032441, -22.041171589), (-85.479855197, -17.284747578))
            ThreePointArc((-85.479855197, -17.284747578), (-80, 0), (-85.479855197, 17.284747578))
            ThreePointArc((-85.479855197, 17.284747578), (-86.028032441, 22.041171589), (-82.326208539, 25.077710319))
        make_face()
        with BuildLine():
            Line((11.471833004, 56.354691343), (53.95175742, 100.616211925))
            ThreePointArc((53.95175742, 100.616211925), (58.303283523, 102.098341173), (62.025791755, 99.401042709))
            ThreePointArc((62.025791755, 99.401042709), (69.877544198, 90.257537939), (81.094875761, 85.850138645))
            ThreePointArc((81.094875761, 85.850138645), (84.866493928, 83.221948595), (84.898130502, 78.625049023))
            Line((84.898130502, 78.625049023), (54.892353403, 19.667982557))
            ThreePointArc((54.892353403, 19.667982557), (50.284966201, 16.9381636), (45.851155545, 19.941703417))
            ThreePointArc((45.851155545, 19.941703417), (32.936806988, 37.61870207), (13.708384523, 48.084095019))
            ThreePointArc((13.708384523, 48.084095019), (10.252590563, 51.587276744), (11.471833004, 56.354691343))
        make_face()
    extrude(amount=REAR_HUB_FLANGE_DEPTH, both=True)

    # Hub Edge Fillet R1 A
    hub_edge_fillet_r1_a_edges = [part_1.edges().sort_by_distance(p)[0] for p in [
        (-81.402759363, 9.066301779, 25),
        (-86.028032441, -22.041171589, 25),
        (-65.735859413, -28.22897003, 25),
        (-44.167091223, -29.4065854, 25),
        (-50, 0, 25),
        (-44.167091223, 29.4065854, 25),
        (-65.735859413, 28.22897003, 25),
        (-86.028032441, 22.041171589, 25),
    ]]
    fillet(hub_edge_fillet_r1_a_edges, radius=HUB_EDGE_FILLET_R1_A_R)

    # Hub Edge Fillet R1 B
    hub_edge_fillet_r1_b_edges = [part_1.edges().sort_by_distance(p)[0] for p in [
        (10.252590563, 51.587276744, 25),
        (32.936806988, 37.61870207, 25),
        (50.284966201, 16.9381636, 25),
        (69.895241952, 49.14651579, 25),
        (84.866493928, 83.221948595, 25),
        (69.877544198, 90.257537939, 25),
        (58.303283523, 102.098341173, 25),
        (32.711795212, 78.485451634, 25),
    ]]
    fillet(hub_edge_fillet_r1_b_edges, radius=HUB_EDGE_FILLET_R1_B_R)

    # Web Arm Cut A Profile → Web Arm Cut A (cut)
    with BuildSketch(Plane.XY.offset(40)):
        with Locations((84.359013574, 110.636130744)):
            Circle(WEB_ARM_CUT_A_PROFILE_R)
        with Locations((84.359013574, 110.636130744)):
            Circle(WEB_ARM_CUT_A_PROFILE_R_2, mode=Mode.SUBTRACT)
    extrude(amount=-WEB_ARM_CUT_A_DEPTH, mode=Mode.SUBTRACT)

    # Web Arm Cut B Profile → Web Arm Cut B (cut)
    with BuildSketch(Plane(origin=(0, 0, 0), x_dir=(-1, 0, 0), z_dir=(0, 0, -1)).offset(WEB_START)):
        with Locations((-84.359013574, 110.636130744)):
            Circle(WEB_ARM_CUT_B_PROFILE_R)
        with Locations(Location((-84.359013574, 110.636130744, 0), (0, 0, 180))):
            Circle(WEB_ARM_CUT_B_PROFILE_R_2, mode=Mode.SUBTRACT)
    extrude(amount=WEB_ARM_CUT_B_DEPTH, mode=Mode.SUBTRACT)


solid = part_1.part
